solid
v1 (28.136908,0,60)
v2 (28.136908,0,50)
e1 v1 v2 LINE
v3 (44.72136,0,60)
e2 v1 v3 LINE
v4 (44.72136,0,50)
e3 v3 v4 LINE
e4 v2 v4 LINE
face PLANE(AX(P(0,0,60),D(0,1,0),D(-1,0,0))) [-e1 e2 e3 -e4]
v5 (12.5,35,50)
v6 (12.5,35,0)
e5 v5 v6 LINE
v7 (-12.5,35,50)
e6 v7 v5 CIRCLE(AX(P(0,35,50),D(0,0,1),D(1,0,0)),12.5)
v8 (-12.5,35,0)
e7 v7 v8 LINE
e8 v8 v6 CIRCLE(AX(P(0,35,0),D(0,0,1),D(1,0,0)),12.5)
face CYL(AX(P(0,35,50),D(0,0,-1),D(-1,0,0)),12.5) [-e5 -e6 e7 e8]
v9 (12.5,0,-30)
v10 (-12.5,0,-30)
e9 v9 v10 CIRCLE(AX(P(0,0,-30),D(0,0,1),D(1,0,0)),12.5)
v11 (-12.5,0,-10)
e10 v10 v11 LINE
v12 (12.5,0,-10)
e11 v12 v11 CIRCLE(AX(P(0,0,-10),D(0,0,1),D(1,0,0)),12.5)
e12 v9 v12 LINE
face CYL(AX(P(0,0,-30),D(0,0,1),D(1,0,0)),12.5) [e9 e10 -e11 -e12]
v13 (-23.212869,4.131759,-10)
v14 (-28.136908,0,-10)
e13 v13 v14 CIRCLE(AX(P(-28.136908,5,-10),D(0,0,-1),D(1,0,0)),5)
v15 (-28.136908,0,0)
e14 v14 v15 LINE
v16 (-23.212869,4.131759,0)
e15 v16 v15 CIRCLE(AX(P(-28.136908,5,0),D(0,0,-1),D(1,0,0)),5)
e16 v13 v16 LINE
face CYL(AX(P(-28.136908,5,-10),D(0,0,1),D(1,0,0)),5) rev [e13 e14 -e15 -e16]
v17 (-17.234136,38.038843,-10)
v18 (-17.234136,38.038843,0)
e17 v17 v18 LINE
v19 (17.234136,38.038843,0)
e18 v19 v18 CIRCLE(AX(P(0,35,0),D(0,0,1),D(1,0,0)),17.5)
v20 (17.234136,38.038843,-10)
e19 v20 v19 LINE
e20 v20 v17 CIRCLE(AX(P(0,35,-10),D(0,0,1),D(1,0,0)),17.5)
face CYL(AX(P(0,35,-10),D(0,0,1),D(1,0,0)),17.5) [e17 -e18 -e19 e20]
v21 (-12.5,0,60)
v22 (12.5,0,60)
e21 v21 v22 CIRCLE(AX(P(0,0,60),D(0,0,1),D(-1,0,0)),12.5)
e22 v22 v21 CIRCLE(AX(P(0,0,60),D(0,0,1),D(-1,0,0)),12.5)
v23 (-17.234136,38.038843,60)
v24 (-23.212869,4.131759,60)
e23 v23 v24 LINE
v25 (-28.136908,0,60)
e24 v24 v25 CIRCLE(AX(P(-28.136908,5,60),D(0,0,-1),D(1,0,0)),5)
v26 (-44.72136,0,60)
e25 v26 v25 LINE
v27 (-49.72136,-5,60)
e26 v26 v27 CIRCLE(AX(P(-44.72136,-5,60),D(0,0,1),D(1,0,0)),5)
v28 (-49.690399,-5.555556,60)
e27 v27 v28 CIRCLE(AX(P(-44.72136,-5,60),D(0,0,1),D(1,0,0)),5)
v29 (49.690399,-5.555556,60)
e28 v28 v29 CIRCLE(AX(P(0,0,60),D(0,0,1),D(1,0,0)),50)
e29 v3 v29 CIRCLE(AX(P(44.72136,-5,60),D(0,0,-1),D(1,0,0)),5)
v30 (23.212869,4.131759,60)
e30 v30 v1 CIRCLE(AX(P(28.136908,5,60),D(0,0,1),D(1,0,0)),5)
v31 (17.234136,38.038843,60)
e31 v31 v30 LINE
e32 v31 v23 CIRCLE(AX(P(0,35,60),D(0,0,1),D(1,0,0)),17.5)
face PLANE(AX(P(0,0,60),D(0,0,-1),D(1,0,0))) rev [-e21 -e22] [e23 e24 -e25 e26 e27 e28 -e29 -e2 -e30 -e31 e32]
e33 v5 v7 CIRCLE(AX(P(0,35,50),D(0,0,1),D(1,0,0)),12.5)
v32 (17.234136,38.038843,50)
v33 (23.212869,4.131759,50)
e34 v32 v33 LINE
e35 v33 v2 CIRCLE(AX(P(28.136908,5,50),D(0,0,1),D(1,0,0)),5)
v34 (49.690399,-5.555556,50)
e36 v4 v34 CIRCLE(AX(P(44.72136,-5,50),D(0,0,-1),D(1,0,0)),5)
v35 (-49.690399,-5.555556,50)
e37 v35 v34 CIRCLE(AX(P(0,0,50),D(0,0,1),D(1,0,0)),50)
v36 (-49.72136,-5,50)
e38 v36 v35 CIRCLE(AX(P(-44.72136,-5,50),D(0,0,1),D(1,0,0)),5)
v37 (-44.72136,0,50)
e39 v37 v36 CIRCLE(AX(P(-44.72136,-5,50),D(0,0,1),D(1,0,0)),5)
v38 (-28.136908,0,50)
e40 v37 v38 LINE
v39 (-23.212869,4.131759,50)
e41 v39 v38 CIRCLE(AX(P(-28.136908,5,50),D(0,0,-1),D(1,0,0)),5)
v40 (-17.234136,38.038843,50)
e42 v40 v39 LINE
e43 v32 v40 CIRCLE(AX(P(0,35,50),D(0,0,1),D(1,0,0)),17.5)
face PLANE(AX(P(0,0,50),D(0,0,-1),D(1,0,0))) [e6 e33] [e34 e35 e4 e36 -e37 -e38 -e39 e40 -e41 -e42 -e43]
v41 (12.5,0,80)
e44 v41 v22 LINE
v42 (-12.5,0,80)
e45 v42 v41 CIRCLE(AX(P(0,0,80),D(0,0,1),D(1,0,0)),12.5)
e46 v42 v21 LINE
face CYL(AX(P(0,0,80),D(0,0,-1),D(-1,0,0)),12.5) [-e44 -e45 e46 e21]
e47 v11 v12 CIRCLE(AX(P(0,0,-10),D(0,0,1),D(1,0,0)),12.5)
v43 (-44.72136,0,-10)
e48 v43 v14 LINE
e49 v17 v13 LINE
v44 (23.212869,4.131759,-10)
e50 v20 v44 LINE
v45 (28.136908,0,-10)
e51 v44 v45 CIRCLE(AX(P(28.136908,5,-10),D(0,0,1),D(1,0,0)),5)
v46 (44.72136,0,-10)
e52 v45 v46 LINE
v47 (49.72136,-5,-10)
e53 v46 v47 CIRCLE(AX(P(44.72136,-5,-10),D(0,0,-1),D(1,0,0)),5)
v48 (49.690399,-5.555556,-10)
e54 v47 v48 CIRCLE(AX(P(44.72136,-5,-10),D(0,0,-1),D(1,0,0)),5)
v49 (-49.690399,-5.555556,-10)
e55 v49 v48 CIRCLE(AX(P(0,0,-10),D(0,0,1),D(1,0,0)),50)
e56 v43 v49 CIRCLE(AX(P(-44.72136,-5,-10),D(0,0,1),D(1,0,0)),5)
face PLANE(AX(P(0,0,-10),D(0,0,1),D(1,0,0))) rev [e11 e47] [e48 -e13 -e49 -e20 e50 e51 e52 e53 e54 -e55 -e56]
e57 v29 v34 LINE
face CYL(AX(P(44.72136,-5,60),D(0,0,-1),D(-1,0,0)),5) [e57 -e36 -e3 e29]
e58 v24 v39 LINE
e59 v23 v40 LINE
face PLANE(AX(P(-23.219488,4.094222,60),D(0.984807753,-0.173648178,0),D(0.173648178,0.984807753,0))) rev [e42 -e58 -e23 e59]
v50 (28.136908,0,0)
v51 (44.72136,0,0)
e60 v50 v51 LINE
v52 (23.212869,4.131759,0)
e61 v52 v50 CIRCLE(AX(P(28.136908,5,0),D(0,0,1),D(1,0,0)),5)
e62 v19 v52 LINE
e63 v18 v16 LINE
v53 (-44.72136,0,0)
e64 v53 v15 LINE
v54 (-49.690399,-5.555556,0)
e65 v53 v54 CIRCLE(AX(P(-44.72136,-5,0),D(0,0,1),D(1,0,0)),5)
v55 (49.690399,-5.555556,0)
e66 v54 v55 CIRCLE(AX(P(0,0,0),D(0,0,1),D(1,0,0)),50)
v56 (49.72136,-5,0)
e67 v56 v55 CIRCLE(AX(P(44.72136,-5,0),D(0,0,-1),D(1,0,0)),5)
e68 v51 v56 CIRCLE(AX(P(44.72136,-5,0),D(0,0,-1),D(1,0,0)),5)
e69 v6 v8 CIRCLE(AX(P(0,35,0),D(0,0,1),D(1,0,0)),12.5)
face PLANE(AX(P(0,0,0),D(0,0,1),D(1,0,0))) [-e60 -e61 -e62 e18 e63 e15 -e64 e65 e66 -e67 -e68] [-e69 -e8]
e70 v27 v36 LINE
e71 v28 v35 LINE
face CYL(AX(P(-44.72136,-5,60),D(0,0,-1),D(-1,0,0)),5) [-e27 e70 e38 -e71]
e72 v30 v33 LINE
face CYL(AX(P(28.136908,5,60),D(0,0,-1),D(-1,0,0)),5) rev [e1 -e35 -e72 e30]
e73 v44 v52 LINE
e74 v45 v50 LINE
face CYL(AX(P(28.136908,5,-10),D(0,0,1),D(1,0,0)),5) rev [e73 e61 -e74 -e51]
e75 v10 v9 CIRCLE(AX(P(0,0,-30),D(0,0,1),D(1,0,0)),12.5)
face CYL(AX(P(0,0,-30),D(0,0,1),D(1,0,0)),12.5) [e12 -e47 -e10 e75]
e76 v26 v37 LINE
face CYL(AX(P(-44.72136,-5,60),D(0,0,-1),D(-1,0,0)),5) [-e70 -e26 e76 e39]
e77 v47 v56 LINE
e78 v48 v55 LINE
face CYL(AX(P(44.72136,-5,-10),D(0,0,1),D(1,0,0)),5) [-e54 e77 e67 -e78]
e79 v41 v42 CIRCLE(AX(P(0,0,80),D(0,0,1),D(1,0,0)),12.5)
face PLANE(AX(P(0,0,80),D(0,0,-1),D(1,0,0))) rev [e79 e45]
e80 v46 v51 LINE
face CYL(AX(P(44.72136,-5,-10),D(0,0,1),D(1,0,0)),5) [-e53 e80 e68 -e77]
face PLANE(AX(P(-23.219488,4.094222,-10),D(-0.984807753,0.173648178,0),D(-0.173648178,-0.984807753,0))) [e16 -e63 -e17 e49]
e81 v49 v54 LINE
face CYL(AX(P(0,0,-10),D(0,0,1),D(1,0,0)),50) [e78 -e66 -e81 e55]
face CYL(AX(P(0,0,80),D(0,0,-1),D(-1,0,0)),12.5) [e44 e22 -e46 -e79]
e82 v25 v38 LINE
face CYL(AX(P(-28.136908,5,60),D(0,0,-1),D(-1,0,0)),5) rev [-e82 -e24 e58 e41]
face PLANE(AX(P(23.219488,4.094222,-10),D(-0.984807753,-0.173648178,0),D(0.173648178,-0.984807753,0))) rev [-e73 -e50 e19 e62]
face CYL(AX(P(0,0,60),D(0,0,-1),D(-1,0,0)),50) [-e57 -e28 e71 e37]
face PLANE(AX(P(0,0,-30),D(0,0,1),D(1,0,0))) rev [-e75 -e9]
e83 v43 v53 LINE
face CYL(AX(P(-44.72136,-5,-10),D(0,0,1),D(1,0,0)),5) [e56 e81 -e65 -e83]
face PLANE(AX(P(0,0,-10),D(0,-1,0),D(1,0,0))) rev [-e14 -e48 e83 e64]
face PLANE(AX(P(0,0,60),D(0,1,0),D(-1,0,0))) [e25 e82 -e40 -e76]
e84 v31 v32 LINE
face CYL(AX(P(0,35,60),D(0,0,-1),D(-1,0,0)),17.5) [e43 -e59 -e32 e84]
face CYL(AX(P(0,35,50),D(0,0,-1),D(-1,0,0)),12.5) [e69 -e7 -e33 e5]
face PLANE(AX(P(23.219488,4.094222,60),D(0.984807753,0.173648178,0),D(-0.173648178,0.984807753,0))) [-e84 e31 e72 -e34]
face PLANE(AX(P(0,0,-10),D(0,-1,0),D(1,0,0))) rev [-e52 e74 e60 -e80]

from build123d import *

# Parameters (mm, degrees)
CRANK_WEB_DEPTH       = 10
SKETCH1_4_R           = 12.5
MAIN_JOURNAL_DEPTH    = 30
CRANK_PIN_SKETCH_25_R = 12.5
CRANK_PIN_25_DEPTH    = 50


with BuildPart() as part:
    # Crank Web Profile → Crank Web (new body)
    with BuildSketch(Plane.XY):
        with BuildLine():
            Line((-28.136908189, 0), (-44.72135955, 0))
            ThreePointArc((-44.72135955, 0), (-48.448139512, -1.666666667), (-49.6903995, -5.555555556))
            ThreePointArc((-49.6903995, -5.555555556), (0, -50), (49.6903995, -5.555555556))
            ThreePointArc((49.6903995, -5.555555556), (48.448139512, -1.666666667), (44.72135955, 0))
            Line((44.72135955, 0), (28.136908189, 0))
            ThreePointArc((28.136908189, 0), (24.92297014, 1.169777784), (23.212869424, 4.131759112))
            Line((23.212869424, 4.131759112), (17.234135678, 38.038843109))
            ThreePointArc((17.234135678, 38.038843109), (0, 52.5), (-17.234135678, 38.038843109))
            Line((-17.234135678, 38.038843109), (-23.212869424, 4.131759112))
            ThreePointArc((-23.212869424, 4.131759112), (-24.92297014, 1.169777784), (-28.136908189, 0))
        make_face()
    crank_web = extrude(amount=-CRANK_WEB_DEPTH)

    # Sketch1_4 → Main Journal (add)
    with BuildSketch(Plane.XY):
        Circle(SKETCH1_4_R)
    main_journal = extrude(amount=-MAIN_JOURNAL_DEPTH)

    # Crank Pin Sketch _25 → Crank Pin _25 (add)
    with BuildSketch(Plane.XY):
        with Locations((0, 35)):
            Circle(CRANK_PIN_SKETCH_25_R)
    extrude(amount=CRANK_PIN_25_DEPTH)

    # Mirror Web and Journal: Crank Web, Main Journal across plane
    add(crank_web.mirror(Plane.XY.offset(25)))
    add(main_journal.mirror(Plane.XY.offset(25)))


solid = part.part
